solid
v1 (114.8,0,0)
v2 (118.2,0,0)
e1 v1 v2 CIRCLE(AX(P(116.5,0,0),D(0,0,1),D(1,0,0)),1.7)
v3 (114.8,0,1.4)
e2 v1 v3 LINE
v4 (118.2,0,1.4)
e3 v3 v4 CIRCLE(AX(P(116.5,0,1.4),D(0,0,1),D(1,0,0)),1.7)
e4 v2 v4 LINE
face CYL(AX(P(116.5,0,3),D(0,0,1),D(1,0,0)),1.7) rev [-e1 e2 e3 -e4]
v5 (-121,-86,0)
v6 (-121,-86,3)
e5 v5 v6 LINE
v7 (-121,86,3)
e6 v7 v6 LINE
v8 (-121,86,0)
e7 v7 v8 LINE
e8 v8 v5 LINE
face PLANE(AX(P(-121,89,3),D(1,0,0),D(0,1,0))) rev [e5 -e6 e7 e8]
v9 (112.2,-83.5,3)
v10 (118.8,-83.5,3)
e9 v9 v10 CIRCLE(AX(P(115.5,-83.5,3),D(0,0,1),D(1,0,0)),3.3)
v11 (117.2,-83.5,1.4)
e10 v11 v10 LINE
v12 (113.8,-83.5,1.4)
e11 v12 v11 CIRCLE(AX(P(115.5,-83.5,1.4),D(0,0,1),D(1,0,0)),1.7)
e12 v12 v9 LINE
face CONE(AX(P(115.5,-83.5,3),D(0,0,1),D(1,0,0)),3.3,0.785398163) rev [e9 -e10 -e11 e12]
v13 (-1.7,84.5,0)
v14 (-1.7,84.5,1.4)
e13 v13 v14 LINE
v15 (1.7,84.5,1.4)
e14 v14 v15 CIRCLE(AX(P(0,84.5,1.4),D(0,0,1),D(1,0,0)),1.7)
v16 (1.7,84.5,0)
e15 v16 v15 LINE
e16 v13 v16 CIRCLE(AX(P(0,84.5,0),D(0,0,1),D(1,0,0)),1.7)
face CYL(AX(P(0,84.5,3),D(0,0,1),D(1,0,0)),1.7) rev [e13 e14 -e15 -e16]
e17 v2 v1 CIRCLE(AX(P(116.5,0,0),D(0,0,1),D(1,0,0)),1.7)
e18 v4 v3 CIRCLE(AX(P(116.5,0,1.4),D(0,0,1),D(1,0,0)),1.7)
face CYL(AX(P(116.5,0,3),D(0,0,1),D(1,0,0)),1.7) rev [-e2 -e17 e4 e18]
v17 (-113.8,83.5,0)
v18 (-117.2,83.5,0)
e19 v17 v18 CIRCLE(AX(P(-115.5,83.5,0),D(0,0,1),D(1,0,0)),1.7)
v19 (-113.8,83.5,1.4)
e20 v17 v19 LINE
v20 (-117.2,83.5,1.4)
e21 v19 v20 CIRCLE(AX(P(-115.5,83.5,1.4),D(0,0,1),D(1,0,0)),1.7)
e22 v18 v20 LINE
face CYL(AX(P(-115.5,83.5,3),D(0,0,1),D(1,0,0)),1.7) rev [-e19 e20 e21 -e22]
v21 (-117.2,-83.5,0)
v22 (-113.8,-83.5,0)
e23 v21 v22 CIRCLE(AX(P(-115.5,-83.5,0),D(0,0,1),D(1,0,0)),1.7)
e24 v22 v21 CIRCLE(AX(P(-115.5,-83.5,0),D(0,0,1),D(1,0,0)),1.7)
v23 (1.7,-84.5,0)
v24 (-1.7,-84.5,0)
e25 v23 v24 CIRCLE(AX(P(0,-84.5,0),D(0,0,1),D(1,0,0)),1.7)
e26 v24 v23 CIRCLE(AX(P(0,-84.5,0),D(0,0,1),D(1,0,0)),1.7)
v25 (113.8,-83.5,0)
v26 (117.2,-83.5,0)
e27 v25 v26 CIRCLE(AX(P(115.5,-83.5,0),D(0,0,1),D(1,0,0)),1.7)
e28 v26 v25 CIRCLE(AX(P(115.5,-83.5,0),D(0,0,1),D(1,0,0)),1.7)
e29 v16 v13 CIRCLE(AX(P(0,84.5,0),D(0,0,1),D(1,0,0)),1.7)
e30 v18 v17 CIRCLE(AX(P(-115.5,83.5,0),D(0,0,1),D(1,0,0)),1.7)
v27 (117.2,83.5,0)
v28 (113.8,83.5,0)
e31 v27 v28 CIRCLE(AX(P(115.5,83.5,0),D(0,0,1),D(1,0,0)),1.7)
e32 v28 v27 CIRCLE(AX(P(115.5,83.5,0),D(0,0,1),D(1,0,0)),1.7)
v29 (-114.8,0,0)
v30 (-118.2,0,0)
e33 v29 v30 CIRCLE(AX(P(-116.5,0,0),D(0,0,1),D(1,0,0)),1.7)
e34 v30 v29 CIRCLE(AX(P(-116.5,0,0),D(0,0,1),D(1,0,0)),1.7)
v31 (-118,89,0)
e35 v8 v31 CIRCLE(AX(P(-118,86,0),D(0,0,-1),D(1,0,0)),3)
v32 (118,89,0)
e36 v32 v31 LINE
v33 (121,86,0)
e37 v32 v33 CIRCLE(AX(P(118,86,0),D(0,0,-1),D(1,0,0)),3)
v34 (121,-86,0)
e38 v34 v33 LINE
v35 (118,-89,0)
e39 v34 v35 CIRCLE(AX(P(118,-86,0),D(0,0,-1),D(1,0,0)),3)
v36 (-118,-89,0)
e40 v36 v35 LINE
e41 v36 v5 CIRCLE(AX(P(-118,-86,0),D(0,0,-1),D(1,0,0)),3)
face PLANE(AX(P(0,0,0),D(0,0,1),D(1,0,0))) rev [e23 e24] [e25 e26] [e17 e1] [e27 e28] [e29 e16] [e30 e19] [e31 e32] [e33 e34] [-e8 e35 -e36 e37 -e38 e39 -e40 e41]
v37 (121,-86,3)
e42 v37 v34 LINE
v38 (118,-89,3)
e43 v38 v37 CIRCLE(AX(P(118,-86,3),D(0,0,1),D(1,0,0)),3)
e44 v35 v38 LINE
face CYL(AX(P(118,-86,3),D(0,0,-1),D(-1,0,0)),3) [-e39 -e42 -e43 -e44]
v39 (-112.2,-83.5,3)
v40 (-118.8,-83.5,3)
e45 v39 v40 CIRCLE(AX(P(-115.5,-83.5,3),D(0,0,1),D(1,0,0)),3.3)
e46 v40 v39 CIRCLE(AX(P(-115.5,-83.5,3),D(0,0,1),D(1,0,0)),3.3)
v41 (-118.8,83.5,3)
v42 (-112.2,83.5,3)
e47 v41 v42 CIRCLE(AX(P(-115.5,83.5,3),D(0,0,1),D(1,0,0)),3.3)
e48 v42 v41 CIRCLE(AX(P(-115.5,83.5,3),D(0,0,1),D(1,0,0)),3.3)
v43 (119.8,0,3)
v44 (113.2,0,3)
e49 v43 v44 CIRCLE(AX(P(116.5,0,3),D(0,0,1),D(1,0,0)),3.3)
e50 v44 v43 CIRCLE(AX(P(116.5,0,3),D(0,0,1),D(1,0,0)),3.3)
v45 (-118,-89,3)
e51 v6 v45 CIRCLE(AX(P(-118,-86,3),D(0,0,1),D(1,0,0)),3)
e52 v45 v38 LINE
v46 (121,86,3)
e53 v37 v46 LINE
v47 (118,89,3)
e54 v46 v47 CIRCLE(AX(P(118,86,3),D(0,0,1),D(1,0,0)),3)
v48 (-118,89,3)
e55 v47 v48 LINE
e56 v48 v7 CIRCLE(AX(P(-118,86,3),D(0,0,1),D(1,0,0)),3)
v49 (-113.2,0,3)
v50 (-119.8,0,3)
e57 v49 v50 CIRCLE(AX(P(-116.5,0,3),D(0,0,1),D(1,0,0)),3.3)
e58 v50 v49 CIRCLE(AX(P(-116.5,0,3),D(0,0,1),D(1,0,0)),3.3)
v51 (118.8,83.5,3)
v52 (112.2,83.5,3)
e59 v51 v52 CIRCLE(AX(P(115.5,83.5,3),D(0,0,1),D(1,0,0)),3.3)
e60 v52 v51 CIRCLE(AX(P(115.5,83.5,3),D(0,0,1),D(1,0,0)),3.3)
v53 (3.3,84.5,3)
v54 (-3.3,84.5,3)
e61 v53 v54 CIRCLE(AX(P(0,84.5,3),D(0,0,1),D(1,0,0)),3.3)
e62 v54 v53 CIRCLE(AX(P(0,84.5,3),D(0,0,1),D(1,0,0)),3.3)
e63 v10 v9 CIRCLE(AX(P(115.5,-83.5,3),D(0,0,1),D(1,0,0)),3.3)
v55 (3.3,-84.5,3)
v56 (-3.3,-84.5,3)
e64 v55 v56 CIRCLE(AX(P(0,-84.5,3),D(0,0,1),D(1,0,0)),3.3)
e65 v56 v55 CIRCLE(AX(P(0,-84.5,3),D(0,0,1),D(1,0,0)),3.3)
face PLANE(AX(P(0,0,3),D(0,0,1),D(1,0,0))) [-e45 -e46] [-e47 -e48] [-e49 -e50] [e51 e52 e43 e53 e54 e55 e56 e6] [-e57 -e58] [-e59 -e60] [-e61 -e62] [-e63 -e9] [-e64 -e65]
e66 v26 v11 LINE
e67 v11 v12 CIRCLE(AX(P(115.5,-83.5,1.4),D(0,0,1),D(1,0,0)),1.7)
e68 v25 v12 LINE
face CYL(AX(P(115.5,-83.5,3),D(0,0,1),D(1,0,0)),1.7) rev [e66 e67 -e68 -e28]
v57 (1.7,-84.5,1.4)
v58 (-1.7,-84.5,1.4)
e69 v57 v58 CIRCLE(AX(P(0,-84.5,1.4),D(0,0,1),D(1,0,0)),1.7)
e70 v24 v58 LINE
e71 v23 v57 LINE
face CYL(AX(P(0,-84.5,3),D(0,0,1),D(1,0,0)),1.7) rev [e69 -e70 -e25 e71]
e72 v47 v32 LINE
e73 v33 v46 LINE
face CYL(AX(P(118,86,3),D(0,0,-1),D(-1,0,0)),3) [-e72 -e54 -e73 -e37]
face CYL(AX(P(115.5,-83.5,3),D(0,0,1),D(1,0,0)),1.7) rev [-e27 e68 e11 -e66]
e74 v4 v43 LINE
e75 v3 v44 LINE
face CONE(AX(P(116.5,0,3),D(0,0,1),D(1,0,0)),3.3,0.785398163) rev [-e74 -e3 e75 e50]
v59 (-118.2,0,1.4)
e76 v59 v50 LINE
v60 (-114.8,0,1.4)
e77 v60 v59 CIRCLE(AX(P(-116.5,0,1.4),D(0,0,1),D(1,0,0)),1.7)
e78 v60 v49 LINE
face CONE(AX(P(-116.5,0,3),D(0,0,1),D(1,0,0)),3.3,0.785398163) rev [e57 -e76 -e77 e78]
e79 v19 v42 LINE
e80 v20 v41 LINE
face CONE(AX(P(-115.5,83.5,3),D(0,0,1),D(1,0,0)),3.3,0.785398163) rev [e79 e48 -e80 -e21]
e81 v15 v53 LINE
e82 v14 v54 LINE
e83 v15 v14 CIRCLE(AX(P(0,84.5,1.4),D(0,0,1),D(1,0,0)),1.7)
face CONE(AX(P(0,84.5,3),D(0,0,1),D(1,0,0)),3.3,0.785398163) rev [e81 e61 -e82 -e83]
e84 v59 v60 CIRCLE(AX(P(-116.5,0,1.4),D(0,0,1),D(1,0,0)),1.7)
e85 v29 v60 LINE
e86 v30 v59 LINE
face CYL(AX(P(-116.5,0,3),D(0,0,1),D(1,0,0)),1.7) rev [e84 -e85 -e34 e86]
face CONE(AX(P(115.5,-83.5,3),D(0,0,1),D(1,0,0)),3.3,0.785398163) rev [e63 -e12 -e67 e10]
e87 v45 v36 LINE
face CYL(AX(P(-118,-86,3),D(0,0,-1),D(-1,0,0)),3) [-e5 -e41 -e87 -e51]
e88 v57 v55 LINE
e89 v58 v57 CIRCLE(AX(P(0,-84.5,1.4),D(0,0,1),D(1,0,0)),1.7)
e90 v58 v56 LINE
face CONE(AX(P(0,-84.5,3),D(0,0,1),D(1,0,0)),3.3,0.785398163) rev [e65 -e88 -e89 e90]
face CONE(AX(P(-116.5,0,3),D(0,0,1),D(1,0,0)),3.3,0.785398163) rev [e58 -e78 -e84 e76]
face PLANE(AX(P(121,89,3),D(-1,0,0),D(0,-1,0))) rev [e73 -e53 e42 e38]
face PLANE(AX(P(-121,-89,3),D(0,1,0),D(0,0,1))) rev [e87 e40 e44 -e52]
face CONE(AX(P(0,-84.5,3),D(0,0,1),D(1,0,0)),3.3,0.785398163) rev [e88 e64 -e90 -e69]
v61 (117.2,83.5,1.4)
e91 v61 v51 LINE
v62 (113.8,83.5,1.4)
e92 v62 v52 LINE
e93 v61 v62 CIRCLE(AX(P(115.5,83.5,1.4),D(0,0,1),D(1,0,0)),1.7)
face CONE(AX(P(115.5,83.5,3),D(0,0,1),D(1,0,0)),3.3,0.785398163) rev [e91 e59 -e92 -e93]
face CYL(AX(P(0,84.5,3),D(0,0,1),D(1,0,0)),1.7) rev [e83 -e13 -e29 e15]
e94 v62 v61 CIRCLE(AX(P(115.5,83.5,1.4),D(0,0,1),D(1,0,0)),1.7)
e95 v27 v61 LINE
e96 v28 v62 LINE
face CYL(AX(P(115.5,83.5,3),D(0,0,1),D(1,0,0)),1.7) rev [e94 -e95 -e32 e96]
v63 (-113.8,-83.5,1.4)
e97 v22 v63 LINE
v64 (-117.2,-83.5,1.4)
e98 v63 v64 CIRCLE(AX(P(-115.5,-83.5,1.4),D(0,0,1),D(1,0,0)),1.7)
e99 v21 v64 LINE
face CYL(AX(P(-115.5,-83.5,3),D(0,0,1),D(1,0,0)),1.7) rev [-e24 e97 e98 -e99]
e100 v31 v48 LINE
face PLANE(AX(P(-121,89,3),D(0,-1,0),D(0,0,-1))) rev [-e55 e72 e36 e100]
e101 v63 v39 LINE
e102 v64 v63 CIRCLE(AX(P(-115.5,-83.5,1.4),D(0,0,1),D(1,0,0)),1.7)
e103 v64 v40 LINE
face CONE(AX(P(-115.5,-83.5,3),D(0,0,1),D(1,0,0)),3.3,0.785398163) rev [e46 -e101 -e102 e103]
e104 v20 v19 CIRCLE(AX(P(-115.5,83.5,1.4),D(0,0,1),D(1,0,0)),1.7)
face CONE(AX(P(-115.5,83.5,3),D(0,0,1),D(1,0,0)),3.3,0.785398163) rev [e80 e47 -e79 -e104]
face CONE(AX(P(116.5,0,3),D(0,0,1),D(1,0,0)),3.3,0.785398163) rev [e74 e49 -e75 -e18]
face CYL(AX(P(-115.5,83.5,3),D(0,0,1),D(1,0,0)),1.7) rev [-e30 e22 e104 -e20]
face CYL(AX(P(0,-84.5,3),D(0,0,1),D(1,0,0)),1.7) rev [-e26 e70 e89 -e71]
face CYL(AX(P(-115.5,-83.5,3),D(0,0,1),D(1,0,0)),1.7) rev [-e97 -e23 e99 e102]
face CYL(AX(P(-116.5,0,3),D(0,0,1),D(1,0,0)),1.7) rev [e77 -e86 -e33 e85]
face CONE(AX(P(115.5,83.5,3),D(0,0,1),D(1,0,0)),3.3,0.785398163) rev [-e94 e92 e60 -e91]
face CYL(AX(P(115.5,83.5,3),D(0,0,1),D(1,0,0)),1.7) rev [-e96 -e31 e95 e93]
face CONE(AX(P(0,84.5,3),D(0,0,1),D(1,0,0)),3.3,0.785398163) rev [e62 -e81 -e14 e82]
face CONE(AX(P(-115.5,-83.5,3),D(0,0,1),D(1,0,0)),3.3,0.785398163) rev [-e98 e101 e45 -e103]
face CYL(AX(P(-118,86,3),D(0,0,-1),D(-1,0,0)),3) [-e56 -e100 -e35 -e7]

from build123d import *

# Parameters (mm, degrees)
SKETCH1_W                                         = 242
SKETCH1_H                                         = 178
BOSS_EXTRUDE1_DEPTH                               = 3
FILLET1_R                                         = 3
HOLE_SIZE_PER_CROSS_FOR_HALF_COUNTERS_D           = 3.4
HOLE_SIZE_PER_CROSS_FOR_HALF_COUNTERS_DEPTH       = 20
HOLE_SIZE_PER_CROSS_FOR_HALF_COUNTERS_CSINK_D     = 6.6
HOLE_SIZE_PER_CROSS_FOR_HALF_COUNTERS_CSINK_ANGLE = 90
HOLE_SIZE_PER_CROSS_FOR_HALF_COUNTERS_TIP         = 1.021463052


with BuildPart() as part:
    # Sketch1 → Boss-Extrude1 (new body)
    with BuildSketch(Plane.XY):
        Rectangle(SKETCH1_W, SKETCH1_H)
    extrude(amount=BOSS_EXTRUDE1_DEPTH)

    # Fillet1
    fillet1_edges = [part.edges().sort_by_distance(p)[0] for p in [
        (121, -89, 1.5),
        (-121, -89, 1.5),
        (-121, 89, 1.5),
        (121, 89, 1.5),
    ]]
    fillet(fillet1_edges, radius=FILLET1_R)

    # Hole size (% per cross) for half-countersunk slotted wood screw, type 1
    with Locations(Plane.XY.offset(3)):
        with Locations((0, 84.5), (-116.5, 0), (0, -84.5), (116.5, 0), (-115.5, 83.5), (-115.5, -83.5), (115.5, -83.5), (115.5, 83.5)):
            CounterSinkHole(HOLE_SIZE_PER_CROSS_FOR_HALF_COUNTERS_D / 2, HOLE_SIZE_PER_CROSS_FOR_HALF_COUNTERS_CSINK_D / 2, depth=HOLE_SIZE_PER_CROSS_FOR_HALF_COUNTERS_DEPTH, counter_sink_angle=HOLE_SIZE_PER_CROSS_FOR_HALF_COUNTERS_CSINK_ANGLE)
            with Locations((0, 0, -(HOLE_SIZE_PER_CROSS_FOR_HALF_COUNTERS_DEPTH + HOLE_SIZE_PER_CROSS_FOR_HALF_COUNTERS_TIP / 2))):  # 118° drill point
                Cone(0, HOLE_SIZE_PER_CROSS_FOR_HALF_COUNTERS_D / 2, HOLE_SIZE_PER_CROSS_FOR_HALF_COUNTERS_TIP, mode=Mode.SUBTRACT)


solid = part.part
